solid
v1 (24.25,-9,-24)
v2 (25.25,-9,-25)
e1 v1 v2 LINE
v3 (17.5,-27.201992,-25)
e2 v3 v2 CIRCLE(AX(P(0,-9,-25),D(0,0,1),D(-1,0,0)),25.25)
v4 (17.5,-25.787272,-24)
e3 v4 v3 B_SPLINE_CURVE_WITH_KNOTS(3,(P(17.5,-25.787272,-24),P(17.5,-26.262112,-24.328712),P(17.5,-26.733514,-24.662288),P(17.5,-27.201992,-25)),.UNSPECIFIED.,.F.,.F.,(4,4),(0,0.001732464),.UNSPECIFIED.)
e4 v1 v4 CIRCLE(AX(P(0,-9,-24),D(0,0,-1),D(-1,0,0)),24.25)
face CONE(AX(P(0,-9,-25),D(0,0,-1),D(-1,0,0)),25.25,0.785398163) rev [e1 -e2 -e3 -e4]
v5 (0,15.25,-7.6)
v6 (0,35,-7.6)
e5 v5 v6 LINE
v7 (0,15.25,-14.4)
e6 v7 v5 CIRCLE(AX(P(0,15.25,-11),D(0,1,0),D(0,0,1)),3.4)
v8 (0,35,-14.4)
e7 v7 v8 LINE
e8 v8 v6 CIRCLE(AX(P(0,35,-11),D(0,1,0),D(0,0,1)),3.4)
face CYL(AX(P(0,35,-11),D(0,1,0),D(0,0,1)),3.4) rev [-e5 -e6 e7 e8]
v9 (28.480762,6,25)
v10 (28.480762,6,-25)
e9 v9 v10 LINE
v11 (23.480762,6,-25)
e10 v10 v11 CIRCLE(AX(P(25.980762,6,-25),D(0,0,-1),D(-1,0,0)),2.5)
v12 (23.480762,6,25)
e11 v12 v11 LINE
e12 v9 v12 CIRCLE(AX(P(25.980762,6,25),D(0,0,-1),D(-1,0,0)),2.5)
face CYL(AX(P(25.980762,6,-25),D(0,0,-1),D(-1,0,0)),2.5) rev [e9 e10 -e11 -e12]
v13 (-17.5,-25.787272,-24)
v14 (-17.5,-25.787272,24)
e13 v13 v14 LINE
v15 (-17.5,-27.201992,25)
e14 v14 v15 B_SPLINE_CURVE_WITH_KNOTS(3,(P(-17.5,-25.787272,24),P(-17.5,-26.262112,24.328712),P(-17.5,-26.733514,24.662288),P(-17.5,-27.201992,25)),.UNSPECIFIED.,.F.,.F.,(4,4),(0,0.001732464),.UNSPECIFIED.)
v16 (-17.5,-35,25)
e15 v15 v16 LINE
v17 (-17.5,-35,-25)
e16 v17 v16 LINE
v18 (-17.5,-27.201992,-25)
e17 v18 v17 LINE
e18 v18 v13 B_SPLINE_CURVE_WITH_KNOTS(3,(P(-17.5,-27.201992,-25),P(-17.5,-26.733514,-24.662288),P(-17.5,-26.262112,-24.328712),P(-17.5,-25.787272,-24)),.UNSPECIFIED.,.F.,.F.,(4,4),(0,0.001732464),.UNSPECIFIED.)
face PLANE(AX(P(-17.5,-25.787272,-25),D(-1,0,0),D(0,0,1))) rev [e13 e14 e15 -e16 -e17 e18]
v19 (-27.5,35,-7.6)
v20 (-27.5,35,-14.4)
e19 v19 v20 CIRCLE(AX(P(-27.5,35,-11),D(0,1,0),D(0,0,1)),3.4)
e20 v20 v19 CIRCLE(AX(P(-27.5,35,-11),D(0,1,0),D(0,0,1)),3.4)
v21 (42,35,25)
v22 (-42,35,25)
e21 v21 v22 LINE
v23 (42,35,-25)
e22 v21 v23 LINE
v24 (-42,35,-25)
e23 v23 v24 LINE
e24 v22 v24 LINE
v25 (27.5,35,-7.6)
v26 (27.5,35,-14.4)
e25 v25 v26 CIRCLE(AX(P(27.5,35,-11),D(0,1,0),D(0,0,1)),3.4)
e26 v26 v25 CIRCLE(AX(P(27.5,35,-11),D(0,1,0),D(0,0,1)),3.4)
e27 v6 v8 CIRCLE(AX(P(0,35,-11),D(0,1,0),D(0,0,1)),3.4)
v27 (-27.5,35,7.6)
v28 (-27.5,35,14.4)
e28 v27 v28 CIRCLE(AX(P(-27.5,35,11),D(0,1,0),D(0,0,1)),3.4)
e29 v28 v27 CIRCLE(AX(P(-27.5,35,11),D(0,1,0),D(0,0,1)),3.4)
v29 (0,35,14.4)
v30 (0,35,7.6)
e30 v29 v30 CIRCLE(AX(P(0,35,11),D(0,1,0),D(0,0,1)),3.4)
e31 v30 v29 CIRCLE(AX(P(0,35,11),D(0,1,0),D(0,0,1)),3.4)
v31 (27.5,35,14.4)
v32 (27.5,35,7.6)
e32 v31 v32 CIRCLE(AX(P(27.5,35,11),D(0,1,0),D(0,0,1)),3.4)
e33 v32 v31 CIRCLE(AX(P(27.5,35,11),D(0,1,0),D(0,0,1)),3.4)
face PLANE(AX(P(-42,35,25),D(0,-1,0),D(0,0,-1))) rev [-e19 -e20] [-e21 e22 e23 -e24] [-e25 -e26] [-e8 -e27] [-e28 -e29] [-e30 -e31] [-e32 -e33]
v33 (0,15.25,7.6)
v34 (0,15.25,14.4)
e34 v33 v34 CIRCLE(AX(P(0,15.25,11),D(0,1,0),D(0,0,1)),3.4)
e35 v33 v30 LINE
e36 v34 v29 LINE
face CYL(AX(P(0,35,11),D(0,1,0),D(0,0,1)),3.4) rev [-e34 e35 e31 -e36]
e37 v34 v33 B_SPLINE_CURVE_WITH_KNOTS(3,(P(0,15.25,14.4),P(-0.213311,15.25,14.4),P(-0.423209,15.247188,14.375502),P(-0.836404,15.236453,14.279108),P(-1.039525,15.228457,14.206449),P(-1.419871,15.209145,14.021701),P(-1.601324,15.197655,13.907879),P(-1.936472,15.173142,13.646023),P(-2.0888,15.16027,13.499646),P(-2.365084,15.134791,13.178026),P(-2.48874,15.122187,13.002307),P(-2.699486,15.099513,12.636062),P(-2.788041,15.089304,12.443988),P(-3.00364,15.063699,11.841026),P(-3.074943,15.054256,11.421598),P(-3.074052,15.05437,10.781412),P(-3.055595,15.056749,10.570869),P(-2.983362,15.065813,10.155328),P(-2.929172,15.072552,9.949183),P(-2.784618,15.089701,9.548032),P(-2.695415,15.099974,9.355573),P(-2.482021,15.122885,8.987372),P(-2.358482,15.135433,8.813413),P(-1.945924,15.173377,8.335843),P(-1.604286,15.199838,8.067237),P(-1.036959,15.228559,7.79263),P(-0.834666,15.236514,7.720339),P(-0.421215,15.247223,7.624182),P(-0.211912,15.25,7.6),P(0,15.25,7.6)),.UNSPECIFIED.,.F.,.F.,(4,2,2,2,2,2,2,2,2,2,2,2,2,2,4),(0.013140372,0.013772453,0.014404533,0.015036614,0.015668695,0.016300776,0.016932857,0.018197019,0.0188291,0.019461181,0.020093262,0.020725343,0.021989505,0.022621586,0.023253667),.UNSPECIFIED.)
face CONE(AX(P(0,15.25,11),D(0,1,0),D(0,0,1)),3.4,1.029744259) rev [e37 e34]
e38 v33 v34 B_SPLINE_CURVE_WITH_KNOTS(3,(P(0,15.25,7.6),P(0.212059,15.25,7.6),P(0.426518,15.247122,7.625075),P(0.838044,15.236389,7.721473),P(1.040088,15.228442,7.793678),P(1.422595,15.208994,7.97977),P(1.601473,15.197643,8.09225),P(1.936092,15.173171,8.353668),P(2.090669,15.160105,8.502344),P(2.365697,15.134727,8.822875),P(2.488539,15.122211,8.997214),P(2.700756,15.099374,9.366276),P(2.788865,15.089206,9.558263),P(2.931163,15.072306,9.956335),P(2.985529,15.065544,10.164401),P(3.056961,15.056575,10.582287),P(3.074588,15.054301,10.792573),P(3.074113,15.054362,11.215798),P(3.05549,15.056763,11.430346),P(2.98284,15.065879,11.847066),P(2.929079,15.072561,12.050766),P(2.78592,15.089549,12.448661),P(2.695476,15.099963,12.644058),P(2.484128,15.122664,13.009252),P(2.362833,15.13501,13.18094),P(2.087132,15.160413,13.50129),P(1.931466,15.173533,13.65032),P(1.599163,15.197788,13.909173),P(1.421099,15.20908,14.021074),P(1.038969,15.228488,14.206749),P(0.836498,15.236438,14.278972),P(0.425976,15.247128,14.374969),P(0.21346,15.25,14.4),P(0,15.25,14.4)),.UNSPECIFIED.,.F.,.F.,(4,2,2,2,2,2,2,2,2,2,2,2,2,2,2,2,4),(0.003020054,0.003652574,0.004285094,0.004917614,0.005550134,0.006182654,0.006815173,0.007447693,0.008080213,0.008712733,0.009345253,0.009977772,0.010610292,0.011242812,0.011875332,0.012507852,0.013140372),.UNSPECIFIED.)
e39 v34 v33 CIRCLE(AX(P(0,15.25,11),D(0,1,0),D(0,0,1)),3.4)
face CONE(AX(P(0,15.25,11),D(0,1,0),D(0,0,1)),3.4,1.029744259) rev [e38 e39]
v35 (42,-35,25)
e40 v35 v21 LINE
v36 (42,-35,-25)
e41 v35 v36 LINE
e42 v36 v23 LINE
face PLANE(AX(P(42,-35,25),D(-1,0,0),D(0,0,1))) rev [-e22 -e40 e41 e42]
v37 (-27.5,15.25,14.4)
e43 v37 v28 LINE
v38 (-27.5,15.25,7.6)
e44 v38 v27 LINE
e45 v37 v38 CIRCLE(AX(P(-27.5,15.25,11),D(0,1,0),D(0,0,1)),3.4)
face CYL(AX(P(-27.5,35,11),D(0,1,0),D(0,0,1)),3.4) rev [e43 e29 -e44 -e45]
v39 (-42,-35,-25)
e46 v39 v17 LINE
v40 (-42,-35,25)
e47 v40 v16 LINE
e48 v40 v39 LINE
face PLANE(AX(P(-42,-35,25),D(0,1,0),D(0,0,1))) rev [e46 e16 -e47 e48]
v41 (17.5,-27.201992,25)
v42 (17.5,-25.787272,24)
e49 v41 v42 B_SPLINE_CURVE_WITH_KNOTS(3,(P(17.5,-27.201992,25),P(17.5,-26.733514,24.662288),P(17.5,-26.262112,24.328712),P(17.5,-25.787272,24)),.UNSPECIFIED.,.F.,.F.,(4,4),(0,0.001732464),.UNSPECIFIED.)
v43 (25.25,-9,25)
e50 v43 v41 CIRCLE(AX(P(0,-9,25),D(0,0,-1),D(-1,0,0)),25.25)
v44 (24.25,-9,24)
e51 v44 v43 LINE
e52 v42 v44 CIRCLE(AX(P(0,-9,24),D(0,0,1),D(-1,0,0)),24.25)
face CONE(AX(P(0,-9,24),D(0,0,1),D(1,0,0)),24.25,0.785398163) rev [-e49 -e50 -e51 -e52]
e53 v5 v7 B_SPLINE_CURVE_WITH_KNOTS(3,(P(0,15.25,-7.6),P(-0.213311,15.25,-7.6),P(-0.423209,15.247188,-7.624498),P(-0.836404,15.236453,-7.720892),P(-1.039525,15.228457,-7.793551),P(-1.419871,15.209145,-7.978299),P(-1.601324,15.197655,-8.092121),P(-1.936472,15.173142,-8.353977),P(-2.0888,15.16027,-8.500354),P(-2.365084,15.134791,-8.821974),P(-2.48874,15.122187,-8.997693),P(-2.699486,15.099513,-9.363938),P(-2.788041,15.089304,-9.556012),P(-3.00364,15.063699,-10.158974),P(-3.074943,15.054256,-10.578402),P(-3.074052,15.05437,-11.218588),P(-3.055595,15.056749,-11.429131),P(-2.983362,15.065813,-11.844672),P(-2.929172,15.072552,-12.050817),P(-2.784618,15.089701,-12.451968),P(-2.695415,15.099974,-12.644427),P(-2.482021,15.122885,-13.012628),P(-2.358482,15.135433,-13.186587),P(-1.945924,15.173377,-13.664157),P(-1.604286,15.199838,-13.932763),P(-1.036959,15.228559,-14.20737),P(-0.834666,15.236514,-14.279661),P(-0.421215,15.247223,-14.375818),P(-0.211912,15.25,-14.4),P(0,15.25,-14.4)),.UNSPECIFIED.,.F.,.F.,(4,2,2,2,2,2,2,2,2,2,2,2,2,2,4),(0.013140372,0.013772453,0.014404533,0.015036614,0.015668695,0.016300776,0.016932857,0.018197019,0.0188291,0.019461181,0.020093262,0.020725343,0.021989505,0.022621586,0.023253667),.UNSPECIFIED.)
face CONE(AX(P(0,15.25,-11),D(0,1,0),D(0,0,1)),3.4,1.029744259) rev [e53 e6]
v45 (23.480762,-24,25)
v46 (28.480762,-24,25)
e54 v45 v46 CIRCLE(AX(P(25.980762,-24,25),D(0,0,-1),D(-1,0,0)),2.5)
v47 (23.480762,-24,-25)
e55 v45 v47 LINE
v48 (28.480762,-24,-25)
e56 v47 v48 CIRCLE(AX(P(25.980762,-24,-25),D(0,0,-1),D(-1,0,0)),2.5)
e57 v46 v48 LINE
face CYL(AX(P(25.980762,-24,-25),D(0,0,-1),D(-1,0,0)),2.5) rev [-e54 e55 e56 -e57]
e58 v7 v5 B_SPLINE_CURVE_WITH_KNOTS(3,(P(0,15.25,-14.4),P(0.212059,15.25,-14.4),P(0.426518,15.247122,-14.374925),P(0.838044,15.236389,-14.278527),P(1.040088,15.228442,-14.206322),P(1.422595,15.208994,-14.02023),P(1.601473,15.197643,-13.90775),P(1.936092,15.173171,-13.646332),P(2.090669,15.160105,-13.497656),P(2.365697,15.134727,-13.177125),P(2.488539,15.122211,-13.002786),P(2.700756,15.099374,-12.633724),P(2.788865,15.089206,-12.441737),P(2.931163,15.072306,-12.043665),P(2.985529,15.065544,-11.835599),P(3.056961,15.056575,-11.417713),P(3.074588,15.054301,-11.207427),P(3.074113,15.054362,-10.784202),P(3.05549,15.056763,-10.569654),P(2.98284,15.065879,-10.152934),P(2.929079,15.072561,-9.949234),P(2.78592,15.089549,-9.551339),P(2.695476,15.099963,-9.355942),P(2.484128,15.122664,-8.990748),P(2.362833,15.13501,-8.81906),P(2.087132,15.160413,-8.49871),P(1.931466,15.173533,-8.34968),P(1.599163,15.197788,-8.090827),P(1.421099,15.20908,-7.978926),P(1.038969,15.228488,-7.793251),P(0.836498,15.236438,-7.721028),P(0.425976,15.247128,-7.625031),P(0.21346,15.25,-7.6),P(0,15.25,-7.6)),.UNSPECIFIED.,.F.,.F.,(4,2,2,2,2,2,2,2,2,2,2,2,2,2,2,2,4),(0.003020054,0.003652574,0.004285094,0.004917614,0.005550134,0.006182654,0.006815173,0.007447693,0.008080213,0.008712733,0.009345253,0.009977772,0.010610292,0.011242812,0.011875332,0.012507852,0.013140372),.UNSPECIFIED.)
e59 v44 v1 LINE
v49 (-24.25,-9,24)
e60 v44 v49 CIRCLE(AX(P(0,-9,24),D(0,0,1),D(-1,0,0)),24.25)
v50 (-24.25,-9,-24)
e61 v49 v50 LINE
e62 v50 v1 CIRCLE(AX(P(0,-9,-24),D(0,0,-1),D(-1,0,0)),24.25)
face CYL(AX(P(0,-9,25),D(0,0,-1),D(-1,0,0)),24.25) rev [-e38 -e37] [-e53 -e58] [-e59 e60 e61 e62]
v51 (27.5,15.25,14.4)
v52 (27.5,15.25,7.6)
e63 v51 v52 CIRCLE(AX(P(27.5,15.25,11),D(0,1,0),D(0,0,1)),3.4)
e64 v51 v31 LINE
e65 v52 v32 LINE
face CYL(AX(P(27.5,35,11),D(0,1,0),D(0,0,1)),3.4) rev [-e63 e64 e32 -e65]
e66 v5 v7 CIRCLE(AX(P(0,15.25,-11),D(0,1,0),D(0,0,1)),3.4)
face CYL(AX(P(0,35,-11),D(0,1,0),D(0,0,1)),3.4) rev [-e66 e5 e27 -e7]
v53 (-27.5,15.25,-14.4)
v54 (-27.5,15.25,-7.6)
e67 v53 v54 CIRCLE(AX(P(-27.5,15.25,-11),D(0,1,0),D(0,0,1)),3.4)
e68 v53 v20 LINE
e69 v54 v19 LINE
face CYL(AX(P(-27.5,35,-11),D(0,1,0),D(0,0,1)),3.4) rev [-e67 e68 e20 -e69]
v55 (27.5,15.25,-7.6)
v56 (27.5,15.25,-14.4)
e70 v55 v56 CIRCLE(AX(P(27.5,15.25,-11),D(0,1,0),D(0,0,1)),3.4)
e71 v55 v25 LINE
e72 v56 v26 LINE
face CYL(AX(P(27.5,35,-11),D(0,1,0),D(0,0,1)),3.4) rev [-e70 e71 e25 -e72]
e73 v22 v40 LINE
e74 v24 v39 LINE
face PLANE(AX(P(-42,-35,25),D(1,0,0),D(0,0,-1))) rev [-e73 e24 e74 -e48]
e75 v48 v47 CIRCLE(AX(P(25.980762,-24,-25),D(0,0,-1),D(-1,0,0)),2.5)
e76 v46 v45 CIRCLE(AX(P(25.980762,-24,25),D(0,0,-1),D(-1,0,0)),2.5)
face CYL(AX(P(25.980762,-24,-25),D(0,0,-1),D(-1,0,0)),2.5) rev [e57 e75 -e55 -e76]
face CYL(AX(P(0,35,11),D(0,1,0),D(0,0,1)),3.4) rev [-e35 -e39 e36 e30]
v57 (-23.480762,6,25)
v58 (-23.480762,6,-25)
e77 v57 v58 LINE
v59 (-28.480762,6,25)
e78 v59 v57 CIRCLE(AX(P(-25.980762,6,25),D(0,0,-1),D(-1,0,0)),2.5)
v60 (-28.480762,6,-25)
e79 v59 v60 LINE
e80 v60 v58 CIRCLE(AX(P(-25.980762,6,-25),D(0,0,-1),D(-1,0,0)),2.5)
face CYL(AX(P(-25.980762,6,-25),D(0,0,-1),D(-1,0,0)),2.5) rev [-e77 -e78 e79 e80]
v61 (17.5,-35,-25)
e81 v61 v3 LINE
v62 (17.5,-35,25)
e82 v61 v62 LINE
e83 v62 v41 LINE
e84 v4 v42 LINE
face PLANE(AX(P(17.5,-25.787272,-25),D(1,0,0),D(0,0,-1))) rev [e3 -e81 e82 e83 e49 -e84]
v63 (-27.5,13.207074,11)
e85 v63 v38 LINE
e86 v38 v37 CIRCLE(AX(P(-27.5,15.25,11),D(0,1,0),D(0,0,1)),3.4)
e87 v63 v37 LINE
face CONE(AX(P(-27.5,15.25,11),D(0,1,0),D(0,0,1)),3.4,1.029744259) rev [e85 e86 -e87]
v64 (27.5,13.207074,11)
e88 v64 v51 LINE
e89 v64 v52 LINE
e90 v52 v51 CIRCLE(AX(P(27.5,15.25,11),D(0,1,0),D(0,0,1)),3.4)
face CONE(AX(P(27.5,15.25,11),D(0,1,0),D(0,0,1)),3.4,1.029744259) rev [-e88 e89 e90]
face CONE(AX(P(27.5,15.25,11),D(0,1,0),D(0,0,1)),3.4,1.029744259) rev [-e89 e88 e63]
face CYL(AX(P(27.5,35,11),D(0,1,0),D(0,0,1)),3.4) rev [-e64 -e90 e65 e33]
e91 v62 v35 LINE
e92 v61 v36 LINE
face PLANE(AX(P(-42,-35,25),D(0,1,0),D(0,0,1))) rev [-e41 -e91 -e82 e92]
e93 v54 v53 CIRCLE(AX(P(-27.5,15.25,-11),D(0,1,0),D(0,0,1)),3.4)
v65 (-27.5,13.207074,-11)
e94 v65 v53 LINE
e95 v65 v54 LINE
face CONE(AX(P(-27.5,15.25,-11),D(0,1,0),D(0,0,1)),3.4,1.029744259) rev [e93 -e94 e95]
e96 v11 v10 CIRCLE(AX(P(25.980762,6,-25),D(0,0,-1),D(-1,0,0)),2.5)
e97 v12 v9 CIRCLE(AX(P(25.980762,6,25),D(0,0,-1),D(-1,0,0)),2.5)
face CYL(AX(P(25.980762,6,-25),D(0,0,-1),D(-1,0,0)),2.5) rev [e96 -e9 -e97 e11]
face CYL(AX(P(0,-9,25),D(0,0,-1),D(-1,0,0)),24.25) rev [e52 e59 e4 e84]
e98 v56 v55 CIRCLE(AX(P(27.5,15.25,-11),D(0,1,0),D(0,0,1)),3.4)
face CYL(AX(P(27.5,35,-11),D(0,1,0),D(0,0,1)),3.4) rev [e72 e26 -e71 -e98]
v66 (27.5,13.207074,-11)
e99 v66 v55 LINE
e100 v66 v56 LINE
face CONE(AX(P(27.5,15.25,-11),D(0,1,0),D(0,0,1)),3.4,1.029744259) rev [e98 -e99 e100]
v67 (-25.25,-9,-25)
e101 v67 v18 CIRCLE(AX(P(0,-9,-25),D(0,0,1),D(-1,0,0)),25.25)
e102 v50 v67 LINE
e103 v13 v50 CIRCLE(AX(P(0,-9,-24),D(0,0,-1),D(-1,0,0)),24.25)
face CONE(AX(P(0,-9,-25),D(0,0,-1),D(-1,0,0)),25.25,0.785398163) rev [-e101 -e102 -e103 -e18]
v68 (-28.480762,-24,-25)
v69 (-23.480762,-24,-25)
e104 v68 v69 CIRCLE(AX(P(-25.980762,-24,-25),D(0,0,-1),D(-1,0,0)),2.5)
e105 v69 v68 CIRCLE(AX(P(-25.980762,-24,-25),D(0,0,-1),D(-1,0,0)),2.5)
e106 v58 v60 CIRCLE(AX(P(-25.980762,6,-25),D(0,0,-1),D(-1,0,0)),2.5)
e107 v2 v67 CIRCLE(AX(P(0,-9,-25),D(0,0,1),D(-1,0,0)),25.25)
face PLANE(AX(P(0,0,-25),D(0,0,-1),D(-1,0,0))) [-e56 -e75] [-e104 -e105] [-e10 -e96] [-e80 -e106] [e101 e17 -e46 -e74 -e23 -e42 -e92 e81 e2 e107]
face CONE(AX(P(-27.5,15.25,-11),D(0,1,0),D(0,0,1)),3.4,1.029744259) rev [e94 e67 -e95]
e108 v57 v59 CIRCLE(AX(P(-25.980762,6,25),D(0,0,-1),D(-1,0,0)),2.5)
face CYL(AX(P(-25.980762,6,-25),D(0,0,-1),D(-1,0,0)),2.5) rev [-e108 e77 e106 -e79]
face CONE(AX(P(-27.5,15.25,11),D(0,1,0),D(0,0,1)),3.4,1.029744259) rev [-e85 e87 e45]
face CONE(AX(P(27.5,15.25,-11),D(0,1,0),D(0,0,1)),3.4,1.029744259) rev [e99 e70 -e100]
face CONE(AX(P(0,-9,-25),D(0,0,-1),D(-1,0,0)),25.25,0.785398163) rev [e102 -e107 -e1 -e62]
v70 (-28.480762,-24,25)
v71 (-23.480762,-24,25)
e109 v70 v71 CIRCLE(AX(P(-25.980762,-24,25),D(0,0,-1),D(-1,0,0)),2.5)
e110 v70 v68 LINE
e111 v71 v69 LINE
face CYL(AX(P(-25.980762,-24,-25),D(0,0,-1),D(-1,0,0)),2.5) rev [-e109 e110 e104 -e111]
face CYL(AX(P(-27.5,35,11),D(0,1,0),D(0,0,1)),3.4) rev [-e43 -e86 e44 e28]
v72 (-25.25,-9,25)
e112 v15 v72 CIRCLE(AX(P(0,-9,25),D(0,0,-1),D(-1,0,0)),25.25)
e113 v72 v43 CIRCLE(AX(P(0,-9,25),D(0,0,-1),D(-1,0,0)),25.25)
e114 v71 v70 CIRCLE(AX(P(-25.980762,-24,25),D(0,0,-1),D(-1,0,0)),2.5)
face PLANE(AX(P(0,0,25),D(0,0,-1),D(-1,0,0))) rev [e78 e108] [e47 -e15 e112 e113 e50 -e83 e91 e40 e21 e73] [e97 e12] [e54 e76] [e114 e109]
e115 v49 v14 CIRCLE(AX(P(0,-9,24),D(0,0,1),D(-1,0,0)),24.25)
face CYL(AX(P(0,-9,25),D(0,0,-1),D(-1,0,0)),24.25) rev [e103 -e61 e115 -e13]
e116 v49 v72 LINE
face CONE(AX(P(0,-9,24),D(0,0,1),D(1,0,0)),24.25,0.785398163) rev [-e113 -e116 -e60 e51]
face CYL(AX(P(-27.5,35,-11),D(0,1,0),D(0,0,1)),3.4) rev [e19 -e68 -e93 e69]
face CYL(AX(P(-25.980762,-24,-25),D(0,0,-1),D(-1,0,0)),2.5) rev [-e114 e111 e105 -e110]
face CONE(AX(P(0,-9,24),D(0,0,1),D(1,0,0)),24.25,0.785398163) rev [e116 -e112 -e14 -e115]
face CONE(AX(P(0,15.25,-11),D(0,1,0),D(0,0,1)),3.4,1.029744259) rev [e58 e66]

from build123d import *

# Parameters (mm, degrees)
SKETCH_1_W             = 84
SKETCH_1_H             = 70
SKETCH_1_R             = 24.25
EXTRUDE_1_DEPTH        = 25
SKETCH_2_W             = 35
SKETCH_2_H             = 9.212728036
CUT_EXTRUDE_1_DEPTH    = 75.087785768
HOLE_WIZARD_M6_1_D     = 5
HOLE_WIZARD_M8_1_D     = 6.8
HOLE_WIZARD_M8_1_DEPTH = 19.75
HOLE_WIZARD_M8_1_TIP   = 2.042926105
CHAMFER_2_SIZE         = 1


with BuildPart() as part:
    # 草图1 → 凸台-拉伸1 (new, symmetric)
    with BuildSketch(Plane.XY):
        Rectangle(SKETCH_1_W, SKETCH_1_H)
        with Locations((0, -9)):
            Circle(SKETCH_1_R, mode=Mode.SUBTRACT)
    extrude(amount=EXTRUDE_1_DEPTH, both=True)

    # 草图2 → 切除-拉伸1 (cut, through all)
    with BuildSketch(Plane.XY.offset(25)):
        with Locations((0, -30.393635982)):
            Rectangle(SKETCH_2_W, SKETCH_2_H)
    extrude(amount=-CUT_EXTRUDE_1_DEPTH, mode=Mode.SUBTRACT)

    # M6 螺纹孔1 (through all)
    with Locations(Plane(origin=(0, 0, -25), x_dir=(-1, 0, 0), z_dir=(0, 0, -1))):
        with Locations((-25.980762114, 6), (25.980762114, 6), (25.980762114, -24), (-25.980762114, -24)):
            Hole(HOLE_WIZARD_M6_1_D / 2)

    # M8 螺纹孔1
    with Locations(Plane(origin=(0, 35, 0), x_dir=(1, 0, 0), z_dir=(0, 1, 0))):
        with Locations((-27.5, 11), (-27.5, -11), (27.5, -11), (27.5, 11), (0, 11), (0, -11)):
            Hole(HOLE_WIZARD_M8_1_D / 2, depth=HOLE_WIZARD_M8_1_DEPTH)
            with Locations((0, 0, -(HOLE_WIZARD_M8_1_DEPTH + HOLE_WIZARD_M8_1_TIP / 2))):  # 118° drill point
                Cone(0, HOLE_WIZARD_M8_1_D / 2, HOLE_WIZARD_M8_1_TIP, mode=Mode.SUBTRACT)

    # 倒角2
    chamfer_2_edges = [part.edges().sort_by_distance(p)[0] for p in [
        (0, 15.25, 25),
        (0, 15.25, -25),
    ]]
    chamfer(chamfer_2_edges, length=CHAMFER_2_SIZE)


solid = part.part
